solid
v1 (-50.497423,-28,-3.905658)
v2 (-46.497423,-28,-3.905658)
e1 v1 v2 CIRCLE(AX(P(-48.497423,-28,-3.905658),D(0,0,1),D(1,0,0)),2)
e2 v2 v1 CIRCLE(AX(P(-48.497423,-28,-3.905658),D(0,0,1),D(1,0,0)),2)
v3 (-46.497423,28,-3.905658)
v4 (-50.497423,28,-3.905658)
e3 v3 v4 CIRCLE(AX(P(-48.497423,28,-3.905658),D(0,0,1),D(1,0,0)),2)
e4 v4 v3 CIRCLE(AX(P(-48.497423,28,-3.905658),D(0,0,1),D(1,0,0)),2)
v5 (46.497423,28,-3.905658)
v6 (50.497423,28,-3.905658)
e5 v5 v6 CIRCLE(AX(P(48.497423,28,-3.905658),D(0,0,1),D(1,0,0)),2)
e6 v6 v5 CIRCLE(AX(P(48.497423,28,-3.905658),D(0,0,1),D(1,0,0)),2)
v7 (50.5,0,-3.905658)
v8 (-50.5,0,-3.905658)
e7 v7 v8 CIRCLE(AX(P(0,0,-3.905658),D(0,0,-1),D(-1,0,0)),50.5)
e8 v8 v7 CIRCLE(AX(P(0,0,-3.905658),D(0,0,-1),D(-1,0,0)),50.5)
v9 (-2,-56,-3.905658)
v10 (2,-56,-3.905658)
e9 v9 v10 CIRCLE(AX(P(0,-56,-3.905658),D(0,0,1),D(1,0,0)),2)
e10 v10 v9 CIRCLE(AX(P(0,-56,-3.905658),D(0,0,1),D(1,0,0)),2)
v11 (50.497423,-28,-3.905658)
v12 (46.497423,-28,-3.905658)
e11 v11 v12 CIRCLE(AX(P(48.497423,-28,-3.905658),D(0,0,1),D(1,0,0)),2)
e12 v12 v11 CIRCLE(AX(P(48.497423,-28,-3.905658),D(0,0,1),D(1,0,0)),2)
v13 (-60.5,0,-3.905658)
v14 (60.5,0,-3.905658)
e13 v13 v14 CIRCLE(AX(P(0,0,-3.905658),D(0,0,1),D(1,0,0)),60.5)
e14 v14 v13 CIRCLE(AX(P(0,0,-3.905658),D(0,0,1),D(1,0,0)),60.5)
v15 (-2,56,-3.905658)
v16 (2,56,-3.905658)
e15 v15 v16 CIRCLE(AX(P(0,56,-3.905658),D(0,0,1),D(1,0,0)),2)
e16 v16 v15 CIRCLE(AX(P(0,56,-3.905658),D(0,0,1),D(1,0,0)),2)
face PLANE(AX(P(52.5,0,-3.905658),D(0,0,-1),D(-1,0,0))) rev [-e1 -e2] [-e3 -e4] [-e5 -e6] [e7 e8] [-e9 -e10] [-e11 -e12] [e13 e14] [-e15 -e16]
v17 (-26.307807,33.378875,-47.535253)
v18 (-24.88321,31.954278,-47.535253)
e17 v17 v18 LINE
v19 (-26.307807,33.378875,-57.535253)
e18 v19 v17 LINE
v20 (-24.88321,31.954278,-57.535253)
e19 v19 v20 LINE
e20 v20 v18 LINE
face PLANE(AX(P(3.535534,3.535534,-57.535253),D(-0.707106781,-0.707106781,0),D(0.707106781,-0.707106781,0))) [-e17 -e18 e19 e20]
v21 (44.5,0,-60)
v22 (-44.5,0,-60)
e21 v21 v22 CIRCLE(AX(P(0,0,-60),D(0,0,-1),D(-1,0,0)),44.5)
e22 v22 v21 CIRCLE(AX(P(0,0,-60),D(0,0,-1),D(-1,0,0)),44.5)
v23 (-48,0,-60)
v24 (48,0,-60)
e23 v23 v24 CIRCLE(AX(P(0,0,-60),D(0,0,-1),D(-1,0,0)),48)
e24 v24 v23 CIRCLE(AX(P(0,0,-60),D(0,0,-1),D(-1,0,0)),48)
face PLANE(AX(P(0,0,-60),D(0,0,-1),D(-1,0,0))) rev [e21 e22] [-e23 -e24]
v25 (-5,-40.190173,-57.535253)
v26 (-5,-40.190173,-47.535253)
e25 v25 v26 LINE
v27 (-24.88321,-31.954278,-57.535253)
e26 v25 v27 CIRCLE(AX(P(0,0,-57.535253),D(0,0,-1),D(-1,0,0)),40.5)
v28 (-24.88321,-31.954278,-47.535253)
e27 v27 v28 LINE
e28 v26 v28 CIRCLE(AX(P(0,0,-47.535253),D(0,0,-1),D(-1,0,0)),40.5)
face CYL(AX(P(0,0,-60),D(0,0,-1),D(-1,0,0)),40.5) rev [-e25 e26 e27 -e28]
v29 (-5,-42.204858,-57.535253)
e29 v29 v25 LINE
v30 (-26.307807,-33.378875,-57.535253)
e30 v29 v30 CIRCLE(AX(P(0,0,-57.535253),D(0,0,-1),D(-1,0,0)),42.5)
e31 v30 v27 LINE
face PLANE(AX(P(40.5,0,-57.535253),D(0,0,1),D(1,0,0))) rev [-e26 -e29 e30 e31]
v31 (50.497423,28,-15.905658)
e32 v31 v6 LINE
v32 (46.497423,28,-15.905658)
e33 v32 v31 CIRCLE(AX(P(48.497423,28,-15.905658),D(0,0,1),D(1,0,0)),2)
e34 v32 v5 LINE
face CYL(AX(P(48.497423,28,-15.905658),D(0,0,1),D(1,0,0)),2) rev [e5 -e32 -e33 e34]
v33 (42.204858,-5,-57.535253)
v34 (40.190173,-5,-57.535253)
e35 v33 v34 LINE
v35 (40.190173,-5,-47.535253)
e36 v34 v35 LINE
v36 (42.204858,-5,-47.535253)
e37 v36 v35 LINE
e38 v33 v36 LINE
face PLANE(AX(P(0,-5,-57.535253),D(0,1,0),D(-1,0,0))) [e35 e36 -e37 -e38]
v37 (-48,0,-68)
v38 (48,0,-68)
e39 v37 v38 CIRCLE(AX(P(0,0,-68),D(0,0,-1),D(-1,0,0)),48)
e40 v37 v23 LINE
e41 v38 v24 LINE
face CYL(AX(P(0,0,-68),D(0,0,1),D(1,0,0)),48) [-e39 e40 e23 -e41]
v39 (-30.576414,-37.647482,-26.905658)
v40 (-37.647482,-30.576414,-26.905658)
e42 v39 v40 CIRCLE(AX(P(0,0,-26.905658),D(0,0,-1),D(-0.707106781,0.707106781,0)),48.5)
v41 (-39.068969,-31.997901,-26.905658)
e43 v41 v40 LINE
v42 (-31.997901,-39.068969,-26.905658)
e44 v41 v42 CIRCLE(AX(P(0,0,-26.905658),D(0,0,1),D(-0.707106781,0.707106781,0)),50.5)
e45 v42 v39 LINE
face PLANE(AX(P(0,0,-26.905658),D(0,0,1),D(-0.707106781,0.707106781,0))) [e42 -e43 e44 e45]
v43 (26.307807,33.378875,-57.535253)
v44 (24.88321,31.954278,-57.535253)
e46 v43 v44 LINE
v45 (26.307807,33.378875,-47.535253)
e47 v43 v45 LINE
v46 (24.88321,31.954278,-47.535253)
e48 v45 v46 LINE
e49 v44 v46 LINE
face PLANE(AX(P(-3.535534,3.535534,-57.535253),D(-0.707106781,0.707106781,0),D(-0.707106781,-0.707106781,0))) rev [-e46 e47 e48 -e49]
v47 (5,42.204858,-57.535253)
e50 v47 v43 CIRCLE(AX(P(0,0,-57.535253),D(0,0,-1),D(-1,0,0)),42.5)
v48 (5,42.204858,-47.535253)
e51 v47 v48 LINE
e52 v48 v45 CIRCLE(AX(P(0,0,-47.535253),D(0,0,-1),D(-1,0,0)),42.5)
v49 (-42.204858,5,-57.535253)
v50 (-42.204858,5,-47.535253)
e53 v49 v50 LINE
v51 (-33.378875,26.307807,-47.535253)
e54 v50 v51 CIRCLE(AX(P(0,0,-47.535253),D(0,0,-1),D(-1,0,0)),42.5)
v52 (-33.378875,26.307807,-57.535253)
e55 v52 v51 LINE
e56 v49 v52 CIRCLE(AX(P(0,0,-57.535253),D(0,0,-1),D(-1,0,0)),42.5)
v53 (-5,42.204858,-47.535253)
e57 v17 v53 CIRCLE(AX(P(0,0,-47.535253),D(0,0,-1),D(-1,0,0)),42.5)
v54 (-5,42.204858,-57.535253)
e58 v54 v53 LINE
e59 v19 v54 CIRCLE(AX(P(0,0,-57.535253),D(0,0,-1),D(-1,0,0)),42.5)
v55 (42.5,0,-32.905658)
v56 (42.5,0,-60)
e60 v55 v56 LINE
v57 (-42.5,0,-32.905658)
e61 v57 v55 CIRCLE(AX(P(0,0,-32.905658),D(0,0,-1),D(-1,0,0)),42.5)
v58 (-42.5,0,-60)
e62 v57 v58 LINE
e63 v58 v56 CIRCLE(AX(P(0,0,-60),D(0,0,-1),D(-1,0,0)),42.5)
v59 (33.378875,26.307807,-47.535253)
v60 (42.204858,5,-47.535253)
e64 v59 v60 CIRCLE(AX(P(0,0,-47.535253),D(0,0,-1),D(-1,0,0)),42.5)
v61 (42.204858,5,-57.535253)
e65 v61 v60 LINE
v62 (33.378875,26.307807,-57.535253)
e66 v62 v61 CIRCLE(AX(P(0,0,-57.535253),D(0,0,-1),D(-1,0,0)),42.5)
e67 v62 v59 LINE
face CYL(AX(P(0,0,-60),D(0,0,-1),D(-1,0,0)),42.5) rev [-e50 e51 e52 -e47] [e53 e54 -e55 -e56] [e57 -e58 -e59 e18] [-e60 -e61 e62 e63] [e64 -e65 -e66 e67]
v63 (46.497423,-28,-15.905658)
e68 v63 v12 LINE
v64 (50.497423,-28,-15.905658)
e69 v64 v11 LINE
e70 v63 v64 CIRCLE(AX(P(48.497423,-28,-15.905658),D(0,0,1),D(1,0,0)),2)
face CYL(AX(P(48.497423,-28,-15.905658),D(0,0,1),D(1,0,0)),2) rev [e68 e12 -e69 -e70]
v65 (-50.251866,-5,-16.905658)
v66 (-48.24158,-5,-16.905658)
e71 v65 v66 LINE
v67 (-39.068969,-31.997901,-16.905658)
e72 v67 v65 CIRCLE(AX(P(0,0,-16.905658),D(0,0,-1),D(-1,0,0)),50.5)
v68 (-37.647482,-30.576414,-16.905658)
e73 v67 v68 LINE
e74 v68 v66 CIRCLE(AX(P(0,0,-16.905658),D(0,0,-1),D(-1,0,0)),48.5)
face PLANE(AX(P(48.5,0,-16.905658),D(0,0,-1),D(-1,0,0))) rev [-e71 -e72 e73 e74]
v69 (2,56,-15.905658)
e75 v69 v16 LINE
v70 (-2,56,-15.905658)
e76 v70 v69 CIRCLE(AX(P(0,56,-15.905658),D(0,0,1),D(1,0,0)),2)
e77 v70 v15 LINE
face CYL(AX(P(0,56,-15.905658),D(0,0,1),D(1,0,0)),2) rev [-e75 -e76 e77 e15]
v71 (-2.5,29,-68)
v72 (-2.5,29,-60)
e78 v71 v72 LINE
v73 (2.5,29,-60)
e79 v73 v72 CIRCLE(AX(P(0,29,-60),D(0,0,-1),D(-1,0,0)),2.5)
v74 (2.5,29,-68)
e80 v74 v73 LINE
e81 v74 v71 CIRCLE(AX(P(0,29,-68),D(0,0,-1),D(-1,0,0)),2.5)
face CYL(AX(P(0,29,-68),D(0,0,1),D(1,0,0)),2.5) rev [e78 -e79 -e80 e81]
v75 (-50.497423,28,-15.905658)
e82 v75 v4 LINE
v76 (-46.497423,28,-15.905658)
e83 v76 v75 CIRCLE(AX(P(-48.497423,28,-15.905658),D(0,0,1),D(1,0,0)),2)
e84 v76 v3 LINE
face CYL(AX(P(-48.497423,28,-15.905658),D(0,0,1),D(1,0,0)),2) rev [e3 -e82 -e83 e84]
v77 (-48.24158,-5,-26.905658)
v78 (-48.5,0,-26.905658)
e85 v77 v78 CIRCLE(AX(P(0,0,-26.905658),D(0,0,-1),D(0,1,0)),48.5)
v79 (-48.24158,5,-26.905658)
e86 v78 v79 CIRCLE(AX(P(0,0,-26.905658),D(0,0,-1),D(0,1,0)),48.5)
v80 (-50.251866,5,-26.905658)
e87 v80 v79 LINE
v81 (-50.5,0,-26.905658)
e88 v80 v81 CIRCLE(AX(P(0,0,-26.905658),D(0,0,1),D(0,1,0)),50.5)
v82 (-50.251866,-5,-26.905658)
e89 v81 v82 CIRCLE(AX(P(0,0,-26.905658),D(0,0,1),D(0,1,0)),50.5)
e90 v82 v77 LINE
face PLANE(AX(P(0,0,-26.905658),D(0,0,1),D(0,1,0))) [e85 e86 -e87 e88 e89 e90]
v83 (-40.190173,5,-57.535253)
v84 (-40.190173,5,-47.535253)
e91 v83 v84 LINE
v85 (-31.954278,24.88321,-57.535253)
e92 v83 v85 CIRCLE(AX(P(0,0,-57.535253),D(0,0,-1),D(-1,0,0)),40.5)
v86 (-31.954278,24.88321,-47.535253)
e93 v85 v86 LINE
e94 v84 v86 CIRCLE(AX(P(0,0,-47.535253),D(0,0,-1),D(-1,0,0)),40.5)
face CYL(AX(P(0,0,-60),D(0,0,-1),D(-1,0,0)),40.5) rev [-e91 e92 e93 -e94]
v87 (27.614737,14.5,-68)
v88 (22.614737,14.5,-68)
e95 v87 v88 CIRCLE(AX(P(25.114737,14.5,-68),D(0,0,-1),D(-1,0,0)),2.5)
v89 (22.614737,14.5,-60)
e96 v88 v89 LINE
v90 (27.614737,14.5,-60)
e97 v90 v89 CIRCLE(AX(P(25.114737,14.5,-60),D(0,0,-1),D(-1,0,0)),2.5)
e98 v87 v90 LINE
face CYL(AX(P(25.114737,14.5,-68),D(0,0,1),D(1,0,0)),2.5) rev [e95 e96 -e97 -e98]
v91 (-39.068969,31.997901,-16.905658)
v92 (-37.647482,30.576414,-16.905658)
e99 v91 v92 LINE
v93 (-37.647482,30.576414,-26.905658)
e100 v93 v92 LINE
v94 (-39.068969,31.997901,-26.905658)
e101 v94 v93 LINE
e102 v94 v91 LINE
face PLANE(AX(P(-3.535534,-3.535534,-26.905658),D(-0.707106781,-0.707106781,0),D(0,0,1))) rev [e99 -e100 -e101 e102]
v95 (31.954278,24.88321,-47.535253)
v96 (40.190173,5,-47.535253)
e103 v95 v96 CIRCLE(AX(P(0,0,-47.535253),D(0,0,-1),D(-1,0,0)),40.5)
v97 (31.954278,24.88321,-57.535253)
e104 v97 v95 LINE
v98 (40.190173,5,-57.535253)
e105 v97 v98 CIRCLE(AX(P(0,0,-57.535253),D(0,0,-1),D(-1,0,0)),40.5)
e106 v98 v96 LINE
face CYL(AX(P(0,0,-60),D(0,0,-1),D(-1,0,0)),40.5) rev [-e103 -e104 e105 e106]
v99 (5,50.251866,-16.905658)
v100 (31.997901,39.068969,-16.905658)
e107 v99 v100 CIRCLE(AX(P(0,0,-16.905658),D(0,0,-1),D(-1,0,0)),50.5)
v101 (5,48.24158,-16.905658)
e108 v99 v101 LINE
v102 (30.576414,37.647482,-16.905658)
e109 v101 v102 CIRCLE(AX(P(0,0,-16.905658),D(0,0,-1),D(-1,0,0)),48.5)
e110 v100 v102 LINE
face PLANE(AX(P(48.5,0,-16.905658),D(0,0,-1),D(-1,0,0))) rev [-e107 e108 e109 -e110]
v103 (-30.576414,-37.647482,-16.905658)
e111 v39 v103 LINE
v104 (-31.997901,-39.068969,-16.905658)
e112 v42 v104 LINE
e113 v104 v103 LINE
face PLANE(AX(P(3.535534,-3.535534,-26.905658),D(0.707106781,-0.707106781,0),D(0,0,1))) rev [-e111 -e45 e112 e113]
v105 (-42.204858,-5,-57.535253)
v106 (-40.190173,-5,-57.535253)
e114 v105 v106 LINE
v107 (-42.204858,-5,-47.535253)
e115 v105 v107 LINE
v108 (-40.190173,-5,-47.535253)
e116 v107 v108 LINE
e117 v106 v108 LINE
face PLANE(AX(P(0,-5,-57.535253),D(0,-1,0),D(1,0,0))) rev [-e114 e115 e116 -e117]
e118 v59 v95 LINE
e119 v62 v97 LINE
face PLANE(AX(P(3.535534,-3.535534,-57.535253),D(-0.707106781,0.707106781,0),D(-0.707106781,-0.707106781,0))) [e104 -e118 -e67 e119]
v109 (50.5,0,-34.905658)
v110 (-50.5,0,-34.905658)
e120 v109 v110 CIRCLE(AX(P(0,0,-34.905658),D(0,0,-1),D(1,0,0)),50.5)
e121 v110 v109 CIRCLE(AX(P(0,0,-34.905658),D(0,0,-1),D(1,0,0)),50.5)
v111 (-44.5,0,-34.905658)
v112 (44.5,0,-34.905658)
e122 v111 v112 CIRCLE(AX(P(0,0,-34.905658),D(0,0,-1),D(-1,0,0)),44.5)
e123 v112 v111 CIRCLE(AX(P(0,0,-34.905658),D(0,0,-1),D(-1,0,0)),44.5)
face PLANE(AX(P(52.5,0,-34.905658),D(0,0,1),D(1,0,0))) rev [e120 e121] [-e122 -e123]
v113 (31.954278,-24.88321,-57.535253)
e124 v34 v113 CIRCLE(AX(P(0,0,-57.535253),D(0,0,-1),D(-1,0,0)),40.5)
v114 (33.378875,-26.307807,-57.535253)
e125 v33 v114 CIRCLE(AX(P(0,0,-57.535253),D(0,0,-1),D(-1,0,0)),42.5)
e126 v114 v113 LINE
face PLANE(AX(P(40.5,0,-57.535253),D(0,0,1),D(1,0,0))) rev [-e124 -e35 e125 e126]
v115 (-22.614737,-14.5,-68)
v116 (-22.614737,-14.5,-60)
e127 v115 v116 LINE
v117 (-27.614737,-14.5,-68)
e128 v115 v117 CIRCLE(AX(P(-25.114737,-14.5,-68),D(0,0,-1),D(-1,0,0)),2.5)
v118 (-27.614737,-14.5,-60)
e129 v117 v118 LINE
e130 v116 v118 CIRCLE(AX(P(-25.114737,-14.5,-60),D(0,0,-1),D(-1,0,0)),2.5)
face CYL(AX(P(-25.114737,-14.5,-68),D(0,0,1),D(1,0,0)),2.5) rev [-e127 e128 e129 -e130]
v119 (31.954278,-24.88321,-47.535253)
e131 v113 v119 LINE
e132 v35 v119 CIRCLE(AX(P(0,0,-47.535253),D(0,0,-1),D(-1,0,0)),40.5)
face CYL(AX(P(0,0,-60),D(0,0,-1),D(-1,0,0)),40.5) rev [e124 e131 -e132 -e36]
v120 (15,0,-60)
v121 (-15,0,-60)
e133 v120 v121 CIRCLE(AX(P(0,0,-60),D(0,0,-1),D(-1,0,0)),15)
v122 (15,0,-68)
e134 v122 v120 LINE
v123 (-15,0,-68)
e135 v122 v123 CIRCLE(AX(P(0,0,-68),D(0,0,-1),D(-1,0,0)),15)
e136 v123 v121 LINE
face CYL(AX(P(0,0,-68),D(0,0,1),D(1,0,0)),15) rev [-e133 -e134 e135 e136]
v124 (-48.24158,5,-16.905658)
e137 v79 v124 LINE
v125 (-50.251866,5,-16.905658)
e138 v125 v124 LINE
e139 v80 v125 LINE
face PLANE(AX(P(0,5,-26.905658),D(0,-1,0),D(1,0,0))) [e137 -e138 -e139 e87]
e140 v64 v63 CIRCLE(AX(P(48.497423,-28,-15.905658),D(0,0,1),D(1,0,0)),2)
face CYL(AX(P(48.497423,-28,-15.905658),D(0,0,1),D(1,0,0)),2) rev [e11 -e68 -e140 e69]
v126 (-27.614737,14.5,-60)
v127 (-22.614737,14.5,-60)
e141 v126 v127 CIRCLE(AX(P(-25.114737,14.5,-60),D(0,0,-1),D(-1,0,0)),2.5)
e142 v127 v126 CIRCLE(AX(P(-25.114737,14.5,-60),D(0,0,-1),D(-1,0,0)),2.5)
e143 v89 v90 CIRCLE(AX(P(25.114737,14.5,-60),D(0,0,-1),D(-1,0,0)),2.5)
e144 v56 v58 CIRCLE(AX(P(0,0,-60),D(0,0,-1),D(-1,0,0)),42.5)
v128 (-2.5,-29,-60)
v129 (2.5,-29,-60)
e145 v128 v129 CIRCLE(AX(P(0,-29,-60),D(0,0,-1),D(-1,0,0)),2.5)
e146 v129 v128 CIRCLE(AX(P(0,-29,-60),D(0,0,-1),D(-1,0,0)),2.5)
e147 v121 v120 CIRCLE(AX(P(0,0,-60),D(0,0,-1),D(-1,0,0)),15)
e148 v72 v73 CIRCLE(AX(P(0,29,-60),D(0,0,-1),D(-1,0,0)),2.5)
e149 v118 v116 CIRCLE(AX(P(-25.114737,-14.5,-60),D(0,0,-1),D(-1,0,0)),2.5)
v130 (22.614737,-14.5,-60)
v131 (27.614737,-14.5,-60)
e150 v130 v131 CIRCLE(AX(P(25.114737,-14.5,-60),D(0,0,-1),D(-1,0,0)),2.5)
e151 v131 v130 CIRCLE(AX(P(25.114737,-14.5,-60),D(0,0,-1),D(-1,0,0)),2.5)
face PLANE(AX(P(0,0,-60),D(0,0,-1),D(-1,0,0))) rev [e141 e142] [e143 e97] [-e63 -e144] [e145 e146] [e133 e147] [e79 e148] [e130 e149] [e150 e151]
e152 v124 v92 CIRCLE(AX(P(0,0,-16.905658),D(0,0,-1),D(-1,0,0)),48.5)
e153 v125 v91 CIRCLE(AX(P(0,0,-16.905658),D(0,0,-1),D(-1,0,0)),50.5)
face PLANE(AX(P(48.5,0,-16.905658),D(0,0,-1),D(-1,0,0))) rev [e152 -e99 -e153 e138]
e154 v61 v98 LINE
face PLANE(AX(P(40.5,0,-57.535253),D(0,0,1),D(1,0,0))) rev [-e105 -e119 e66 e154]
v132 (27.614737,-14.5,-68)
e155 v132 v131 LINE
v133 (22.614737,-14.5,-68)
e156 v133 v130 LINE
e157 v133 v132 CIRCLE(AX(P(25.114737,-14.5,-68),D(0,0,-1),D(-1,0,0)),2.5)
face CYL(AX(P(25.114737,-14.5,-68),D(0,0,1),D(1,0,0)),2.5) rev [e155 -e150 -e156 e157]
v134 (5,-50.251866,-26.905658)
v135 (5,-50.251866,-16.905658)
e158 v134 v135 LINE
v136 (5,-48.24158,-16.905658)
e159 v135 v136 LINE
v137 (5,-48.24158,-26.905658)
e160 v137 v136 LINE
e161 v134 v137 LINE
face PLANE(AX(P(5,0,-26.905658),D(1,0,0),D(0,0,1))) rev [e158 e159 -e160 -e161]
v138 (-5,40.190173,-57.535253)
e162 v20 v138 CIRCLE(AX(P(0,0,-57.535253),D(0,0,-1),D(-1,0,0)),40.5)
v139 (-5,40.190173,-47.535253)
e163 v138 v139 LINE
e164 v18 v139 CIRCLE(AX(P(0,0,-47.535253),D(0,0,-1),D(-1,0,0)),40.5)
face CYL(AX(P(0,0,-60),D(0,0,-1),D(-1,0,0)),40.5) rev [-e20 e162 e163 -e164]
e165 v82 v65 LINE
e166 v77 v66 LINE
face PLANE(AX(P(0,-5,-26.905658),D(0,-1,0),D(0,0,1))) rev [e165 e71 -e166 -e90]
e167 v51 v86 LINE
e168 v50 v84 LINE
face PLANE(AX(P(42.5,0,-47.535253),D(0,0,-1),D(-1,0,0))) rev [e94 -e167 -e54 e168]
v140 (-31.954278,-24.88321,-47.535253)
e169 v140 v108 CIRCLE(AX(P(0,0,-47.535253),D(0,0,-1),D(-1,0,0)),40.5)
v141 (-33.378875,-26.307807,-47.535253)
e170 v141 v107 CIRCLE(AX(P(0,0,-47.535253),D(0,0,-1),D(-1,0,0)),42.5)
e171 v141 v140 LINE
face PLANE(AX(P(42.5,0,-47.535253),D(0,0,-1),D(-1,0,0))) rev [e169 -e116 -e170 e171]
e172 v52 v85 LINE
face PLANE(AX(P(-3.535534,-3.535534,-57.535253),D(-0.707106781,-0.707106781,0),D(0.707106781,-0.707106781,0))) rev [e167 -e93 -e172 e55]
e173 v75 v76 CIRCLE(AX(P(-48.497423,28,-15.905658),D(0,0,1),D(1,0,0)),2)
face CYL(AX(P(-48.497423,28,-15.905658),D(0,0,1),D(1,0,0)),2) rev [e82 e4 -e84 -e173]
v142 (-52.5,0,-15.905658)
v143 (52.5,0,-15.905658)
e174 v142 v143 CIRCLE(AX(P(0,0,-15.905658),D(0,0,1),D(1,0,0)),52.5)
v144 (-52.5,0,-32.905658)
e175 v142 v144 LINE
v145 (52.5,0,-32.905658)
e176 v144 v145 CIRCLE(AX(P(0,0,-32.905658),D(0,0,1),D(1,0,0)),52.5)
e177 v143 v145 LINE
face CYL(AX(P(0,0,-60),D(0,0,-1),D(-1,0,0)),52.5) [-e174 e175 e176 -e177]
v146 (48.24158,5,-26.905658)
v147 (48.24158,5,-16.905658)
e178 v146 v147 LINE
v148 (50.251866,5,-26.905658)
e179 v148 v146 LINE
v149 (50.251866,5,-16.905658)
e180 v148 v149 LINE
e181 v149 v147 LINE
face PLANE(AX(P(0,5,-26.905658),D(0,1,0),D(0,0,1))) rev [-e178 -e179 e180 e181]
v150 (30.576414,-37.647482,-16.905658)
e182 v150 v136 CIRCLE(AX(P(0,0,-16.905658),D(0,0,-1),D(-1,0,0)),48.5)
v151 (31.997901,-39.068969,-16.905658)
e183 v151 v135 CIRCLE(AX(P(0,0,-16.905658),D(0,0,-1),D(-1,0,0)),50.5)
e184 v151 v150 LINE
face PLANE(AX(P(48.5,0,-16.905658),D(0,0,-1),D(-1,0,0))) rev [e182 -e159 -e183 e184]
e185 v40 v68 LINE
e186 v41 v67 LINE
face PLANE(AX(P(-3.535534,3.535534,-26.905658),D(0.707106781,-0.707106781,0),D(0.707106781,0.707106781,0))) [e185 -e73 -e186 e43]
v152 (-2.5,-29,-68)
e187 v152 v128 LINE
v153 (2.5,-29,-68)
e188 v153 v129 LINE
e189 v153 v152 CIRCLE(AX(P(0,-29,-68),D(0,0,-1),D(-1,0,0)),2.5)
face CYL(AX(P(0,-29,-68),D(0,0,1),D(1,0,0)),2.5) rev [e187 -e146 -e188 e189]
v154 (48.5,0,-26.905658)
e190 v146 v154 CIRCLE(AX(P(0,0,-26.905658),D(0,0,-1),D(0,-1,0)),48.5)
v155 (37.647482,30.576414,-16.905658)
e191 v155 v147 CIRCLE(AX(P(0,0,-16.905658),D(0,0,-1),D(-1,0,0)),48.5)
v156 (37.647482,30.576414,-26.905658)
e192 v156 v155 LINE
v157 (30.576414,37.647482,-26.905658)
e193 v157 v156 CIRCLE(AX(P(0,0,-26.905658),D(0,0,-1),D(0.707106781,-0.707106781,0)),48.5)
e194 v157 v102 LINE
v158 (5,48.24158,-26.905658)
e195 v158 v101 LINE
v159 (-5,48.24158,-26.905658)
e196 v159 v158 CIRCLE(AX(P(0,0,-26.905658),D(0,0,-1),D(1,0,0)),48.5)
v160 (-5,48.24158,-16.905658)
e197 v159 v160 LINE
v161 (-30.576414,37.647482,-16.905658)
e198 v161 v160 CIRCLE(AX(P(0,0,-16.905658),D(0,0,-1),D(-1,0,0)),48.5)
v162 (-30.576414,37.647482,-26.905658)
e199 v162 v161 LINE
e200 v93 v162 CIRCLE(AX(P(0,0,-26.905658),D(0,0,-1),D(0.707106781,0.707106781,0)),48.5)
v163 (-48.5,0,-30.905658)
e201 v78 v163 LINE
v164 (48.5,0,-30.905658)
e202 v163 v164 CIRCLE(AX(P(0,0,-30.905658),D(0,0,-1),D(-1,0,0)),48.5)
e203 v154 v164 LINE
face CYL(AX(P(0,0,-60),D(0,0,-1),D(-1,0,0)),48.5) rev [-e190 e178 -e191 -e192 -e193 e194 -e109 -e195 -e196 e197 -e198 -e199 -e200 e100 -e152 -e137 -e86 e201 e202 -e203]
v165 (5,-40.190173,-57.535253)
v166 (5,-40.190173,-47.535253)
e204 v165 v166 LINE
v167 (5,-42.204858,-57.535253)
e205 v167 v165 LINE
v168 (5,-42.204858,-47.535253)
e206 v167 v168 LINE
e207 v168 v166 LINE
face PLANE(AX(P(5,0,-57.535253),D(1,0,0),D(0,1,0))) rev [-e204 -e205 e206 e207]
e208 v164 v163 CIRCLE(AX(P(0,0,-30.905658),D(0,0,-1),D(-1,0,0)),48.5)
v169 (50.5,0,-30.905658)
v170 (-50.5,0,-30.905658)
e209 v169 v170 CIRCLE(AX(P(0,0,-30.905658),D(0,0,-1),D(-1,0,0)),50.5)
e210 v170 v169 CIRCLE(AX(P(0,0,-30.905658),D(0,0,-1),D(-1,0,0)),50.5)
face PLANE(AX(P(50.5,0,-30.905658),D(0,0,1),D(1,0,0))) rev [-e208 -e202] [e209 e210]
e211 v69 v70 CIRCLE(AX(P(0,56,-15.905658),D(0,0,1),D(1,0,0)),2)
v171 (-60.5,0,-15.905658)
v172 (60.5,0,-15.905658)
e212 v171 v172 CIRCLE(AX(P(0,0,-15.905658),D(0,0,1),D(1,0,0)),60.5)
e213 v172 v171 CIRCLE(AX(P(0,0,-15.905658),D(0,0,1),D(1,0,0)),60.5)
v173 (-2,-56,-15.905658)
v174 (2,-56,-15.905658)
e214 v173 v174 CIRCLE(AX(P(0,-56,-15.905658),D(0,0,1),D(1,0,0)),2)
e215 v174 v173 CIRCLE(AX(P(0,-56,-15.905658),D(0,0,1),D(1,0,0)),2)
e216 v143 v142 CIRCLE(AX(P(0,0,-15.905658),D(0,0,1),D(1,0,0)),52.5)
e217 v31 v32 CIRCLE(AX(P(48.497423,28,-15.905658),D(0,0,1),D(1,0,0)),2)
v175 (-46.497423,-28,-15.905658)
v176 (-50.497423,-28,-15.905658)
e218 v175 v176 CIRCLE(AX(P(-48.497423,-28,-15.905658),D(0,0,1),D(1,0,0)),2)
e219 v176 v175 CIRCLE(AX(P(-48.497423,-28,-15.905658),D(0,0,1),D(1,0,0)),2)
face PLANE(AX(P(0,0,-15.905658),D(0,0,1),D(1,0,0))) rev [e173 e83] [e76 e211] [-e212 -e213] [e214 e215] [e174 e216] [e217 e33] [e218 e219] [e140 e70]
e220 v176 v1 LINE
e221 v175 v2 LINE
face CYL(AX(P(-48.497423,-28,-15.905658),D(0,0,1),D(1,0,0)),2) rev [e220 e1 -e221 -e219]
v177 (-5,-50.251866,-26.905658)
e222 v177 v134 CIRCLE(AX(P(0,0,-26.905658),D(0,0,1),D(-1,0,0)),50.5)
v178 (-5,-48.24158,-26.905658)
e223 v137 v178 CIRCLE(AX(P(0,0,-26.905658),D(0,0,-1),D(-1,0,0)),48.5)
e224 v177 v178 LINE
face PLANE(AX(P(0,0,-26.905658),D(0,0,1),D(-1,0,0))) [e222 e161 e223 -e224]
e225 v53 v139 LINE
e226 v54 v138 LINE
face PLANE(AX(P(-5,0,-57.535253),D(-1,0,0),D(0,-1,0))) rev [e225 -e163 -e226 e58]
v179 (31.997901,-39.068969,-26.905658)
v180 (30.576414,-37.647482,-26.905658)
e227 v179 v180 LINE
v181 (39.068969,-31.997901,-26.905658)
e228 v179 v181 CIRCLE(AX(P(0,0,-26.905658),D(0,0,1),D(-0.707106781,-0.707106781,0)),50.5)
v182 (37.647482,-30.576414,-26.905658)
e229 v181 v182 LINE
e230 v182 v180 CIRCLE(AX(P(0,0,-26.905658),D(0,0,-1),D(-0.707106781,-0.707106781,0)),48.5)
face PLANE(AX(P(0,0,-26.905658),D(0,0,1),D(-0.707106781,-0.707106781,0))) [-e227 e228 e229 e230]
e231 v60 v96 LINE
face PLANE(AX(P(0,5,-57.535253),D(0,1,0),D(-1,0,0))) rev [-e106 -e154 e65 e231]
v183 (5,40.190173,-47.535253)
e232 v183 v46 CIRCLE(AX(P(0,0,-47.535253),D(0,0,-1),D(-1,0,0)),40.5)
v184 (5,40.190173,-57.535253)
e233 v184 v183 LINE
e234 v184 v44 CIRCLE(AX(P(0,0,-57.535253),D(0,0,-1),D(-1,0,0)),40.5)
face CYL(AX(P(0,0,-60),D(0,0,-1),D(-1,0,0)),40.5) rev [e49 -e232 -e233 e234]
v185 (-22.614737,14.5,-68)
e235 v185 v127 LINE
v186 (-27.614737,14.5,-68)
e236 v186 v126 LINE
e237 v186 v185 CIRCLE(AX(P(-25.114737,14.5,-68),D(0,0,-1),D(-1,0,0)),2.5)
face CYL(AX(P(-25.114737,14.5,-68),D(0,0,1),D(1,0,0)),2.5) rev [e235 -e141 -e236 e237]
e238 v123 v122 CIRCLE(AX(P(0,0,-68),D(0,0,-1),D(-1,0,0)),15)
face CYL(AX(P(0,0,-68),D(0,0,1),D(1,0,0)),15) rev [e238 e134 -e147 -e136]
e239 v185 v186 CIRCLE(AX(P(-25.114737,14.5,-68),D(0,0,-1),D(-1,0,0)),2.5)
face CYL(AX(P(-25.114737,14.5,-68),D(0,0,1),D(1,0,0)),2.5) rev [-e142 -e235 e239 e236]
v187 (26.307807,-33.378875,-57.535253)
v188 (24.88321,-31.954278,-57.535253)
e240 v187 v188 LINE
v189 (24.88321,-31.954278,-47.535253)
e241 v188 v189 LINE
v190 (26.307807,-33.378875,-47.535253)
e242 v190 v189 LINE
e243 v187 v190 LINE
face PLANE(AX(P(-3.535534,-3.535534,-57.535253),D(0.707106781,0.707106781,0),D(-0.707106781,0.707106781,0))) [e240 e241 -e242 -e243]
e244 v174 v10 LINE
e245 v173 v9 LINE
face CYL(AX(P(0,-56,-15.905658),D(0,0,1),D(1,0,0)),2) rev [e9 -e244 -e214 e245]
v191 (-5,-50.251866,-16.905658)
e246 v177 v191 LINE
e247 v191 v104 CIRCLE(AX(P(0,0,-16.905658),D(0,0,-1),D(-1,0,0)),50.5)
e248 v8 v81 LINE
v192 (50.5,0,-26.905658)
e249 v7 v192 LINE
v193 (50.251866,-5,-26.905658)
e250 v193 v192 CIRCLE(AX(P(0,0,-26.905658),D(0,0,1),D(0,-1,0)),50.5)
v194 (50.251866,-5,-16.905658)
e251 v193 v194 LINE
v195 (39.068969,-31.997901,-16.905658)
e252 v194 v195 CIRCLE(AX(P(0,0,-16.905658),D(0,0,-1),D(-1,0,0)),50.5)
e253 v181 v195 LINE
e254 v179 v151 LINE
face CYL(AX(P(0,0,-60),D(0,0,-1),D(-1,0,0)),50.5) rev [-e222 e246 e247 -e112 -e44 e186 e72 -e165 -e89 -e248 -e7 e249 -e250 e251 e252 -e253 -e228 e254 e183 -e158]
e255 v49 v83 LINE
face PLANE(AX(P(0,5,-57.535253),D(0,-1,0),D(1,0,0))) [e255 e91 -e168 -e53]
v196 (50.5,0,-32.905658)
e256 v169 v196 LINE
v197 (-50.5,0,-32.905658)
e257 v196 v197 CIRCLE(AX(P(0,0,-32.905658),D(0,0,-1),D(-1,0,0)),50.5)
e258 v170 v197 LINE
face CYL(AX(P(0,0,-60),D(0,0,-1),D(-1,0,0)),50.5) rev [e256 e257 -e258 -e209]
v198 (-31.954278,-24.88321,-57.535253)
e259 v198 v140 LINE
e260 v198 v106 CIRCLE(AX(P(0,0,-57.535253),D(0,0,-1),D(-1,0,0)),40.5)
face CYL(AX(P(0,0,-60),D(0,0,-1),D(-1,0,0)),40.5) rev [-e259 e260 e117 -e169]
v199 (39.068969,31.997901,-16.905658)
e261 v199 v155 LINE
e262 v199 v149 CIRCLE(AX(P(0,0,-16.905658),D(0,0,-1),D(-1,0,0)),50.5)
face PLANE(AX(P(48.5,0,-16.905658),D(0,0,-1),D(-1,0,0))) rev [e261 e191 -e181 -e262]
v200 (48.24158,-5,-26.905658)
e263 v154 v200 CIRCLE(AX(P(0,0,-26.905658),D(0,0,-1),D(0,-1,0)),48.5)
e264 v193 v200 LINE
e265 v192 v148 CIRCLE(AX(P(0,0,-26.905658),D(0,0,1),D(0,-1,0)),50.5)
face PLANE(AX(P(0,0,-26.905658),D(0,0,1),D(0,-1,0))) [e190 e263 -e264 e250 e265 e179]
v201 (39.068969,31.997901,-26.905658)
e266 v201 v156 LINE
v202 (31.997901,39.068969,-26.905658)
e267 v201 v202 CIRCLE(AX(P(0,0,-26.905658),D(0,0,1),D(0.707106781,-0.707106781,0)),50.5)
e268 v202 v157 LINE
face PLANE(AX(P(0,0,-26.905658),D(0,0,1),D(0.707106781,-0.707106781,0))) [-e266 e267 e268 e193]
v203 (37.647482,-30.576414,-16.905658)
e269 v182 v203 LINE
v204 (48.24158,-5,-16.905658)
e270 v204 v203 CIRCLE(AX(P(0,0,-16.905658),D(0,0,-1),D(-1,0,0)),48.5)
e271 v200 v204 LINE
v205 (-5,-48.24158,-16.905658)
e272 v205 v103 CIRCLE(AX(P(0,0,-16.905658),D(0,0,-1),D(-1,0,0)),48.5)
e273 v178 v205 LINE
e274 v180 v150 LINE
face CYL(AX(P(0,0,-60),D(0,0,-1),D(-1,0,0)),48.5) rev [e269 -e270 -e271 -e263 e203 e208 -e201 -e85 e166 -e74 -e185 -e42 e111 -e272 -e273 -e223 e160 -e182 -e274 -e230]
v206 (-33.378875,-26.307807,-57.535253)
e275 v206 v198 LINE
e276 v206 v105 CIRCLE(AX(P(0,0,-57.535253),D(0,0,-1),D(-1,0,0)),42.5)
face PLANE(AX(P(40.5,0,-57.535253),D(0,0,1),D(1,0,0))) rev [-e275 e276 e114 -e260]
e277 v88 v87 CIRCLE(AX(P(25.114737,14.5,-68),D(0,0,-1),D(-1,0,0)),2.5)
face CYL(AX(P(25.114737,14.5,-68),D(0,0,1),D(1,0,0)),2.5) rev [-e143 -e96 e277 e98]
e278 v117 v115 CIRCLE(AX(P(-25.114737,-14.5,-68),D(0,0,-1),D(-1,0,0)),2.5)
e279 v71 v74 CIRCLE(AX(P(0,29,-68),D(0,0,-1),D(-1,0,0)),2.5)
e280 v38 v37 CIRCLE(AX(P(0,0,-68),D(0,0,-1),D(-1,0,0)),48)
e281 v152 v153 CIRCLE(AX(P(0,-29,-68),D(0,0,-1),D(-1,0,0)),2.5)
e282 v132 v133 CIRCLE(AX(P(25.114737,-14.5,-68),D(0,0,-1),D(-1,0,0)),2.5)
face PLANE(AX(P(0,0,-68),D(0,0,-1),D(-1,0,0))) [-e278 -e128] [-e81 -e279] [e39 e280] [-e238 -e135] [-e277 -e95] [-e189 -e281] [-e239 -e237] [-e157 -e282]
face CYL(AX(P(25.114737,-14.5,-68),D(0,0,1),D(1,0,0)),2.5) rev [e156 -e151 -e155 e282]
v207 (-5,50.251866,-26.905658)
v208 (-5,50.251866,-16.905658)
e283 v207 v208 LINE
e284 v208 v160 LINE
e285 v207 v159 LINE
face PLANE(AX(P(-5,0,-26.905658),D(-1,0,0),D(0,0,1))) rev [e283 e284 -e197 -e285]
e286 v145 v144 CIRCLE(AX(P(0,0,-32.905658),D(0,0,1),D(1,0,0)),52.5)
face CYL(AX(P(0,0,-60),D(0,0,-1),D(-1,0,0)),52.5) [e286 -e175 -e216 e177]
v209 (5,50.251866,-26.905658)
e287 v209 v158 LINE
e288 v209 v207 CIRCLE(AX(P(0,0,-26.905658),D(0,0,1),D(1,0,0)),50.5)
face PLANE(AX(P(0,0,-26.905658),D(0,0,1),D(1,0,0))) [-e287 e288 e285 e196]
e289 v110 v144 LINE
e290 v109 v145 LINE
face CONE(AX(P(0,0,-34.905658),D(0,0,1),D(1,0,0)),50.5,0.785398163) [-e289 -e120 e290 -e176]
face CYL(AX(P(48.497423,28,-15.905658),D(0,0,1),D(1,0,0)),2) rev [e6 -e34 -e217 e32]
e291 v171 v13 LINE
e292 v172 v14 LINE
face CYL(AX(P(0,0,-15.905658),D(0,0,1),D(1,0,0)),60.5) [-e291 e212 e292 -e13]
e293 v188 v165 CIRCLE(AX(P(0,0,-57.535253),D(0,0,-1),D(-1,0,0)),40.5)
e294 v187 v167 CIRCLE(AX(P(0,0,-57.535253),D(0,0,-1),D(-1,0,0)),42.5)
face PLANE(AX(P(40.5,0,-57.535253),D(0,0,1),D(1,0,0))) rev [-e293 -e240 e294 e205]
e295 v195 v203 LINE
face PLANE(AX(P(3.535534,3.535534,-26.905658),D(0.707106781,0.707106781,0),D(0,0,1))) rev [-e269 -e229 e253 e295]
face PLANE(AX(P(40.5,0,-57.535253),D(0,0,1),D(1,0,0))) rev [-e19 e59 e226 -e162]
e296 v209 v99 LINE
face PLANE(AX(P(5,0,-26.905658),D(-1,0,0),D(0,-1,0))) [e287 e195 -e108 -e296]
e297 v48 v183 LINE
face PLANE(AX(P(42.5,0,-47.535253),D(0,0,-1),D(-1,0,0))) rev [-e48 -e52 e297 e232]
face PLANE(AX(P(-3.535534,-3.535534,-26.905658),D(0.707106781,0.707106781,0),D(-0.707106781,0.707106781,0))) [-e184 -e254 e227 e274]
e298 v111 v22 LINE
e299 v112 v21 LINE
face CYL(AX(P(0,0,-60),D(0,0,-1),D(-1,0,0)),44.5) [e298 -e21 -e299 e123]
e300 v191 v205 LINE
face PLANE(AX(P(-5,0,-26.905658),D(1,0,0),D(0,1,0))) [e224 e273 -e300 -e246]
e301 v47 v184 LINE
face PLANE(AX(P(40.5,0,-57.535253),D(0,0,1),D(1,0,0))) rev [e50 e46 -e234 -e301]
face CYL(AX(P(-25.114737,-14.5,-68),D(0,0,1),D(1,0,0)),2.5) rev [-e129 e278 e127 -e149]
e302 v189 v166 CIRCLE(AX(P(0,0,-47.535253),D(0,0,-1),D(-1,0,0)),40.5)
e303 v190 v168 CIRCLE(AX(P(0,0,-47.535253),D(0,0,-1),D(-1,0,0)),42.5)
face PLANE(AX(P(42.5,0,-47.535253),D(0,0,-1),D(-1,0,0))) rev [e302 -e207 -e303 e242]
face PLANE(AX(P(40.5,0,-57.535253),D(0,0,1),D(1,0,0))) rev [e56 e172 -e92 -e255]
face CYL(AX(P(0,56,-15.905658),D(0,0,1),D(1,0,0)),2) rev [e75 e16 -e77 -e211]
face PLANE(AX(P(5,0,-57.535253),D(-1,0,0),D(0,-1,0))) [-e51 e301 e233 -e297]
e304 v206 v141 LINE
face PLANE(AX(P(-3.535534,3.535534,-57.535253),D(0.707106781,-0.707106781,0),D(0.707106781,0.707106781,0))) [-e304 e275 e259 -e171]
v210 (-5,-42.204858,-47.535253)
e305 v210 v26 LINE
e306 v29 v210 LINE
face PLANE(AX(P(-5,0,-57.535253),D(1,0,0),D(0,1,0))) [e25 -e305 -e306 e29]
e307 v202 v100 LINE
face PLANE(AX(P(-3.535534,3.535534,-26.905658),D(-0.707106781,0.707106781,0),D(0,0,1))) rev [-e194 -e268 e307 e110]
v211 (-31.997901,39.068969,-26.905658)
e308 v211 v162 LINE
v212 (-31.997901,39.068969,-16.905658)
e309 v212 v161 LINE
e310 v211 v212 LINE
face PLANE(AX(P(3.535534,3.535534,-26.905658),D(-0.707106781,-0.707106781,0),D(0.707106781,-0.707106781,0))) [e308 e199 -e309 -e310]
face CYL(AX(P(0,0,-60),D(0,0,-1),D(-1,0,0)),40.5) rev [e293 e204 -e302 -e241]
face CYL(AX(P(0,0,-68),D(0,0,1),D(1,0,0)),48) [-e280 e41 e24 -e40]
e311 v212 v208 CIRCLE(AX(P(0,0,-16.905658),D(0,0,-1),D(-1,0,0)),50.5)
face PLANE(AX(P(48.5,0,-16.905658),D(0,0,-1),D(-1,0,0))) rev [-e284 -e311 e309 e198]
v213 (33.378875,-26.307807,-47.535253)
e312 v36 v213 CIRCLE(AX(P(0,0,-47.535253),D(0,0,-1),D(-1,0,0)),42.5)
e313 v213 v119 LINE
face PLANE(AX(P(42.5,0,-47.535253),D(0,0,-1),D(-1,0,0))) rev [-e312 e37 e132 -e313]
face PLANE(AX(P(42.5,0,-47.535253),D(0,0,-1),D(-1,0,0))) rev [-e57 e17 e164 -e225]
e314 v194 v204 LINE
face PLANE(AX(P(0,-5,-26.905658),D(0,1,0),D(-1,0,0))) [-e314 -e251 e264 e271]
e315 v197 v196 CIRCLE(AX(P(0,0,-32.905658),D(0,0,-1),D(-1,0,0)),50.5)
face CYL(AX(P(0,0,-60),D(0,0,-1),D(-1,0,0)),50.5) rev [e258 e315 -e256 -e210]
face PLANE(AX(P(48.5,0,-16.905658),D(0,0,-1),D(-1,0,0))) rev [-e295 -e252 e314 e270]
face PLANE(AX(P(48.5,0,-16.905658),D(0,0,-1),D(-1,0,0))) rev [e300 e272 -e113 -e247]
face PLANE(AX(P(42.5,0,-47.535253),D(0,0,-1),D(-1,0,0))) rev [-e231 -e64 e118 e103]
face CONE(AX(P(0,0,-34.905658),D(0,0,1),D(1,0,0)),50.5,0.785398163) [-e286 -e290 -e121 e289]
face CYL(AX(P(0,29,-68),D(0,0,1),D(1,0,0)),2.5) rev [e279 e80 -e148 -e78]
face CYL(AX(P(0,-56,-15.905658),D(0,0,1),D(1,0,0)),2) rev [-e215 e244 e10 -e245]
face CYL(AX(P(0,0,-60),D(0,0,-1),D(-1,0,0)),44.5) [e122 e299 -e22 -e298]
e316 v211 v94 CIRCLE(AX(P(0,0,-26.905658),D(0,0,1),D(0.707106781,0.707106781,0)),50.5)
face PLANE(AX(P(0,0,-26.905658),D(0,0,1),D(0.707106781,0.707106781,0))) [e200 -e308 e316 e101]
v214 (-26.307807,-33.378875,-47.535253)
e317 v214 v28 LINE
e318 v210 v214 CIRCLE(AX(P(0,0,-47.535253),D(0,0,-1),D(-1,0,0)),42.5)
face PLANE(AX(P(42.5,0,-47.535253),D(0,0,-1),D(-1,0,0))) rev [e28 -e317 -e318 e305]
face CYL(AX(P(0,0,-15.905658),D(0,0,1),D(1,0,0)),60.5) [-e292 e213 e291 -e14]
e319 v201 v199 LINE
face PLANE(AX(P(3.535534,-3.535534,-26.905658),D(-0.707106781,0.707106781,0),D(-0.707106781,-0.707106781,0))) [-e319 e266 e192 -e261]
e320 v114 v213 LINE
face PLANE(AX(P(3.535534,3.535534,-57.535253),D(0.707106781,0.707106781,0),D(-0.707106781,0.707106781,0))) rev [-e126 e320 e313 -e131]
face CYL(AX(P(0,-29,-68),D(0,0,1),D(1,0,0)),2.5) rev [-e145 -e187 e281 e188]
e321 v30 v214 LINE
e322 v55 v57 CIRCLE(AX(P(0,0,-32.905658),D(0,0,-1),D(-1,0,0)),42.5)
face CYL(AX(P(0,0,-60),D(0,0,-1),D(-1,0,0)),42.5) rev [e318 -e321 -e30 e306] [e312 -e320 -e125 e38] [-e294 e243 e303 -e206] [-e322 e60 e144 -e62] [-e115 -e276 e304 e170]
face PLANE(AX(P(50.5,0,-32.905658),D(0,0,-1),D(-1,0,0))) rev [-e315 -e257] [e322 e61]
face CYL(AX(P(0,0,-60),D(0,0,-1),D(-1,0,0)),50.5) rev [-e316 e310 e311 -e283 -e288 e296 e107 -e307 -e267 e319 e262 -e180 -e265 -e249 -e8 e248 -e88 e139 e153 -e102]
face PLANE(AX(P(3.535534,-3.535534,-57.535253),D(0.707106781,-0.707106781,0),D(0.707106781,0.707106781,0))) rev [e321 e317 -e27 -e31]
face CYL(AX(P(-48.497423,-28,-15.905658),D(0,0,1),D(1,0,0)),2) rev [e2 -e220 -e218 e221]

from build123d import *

# Parameters (mm, degrees)
CUT_EXTRUDE2_START  = -10
SKETCH3_R           = 40.5
CUT_EXTRUDE2_DEPTH  = 10
CUT_EXTRUDE3_START  = -10
CUT_EXTRUDE3_DEPTH  = 10
CIRPATTERN5_COUNT   = 8
CHAMFER1_SIZE       = 2
SKETCH4_R           = 48
SKETCH4_R_2         = 15
SKETCH4_R_3         = 2.5
BOSS_EXTRUDE1_DEPTH = 8
SKETCH7_R           = 60.5
SKETCH7_R_2         = 52.5
SKETCH7_R_3         = 2
BOSS_EXTRUDE2_DEPTH = 12


with BuildPart() as part:
    # Sketch1 → Revolve1 (revolve)
    with BuildSketch(Plane(origin=(0, 0, 0), x_dir=(1, 0, 0), z_dir=(0, 1, 0)), mode=Mode.PRIVATE) as revolve1_sk:
        Polygon((50.5, 3.905657953), (50.5, 16.905657953), (48.5, 16.905657953), (48.5, 30.905657953), (50.5, 30.905657953), (50.5, 32.905657953), (42.5, 32.905657953), (42.5, 47.535252784), (40.5, 47.535252784), (40.5, 57.535252784), (42.5, 57.535252784), (42.5, 60), (44.5, 60), (44.5, 34.905657953), (52.5, 34.905657953), (52.5, 3.905657953), align=None)
    revolve(revolve1_sk.sketch.rotate(Axis((0, 0, -60), (0, 0, 1)), 180), axis=Axis((0, 0, -60), (0, 0, 1)))

    # Sketch3 → Cut-Extrude2 (cut)
    with BuildSketch(Plane.XY.offset(-47.535252784).offset(CUT_EXTRUDE2_START)):
        with BuildLine():
            ThreePointArc((5, 42.20485754), (0, 42.5), (-5, 42.20485754))
            Line((-5, 42.20485754), (-5, 40.190172928))
            ThreePointArc((-5, 40.190172928), (0, 40.5), (5, 40.190172928))
            Line((5, 40.190172928), (5, 42.20485754))
        make_face()
        with BuildLine():
            ThreePointArc((33.378874872, 26.30780706), (30.0520382, 30.0520382), (26.30780706, 33.378874872))
            Line((26.30780706, 33.378874872), (24.883209909, 31.954277721))
            ThreePointArc((24.883209909, 31.954277721), (28.637824638, 28.637824638), (31.954277721, 24.883209909))
            Line((31.954277721, 24.883209909), (33.378874872, 26.30780706))
        make_face()
        with BuildLine():
            ThreePointArc((42.5, 0), (42.426150223, 2.504351666), (42.20485754, 5))
            Line((42.20485754, 5), (40.190172928, 5))
            ThreePointArc((40.190172928, 5), (40.422469022, 2.504795042), (40.5, 0))
            ThreePointArc((40.5, 0), (40.422469022, -2.504795042), (40.190172928, -5))
            Line((40.190172928, -5), (42.20485754, -5))
            ThreePointArc((42.20485754, -5), (42.426150223, -2.504351666), (42.5, 0))
        make_face()
        with BuildLine():
            ThreePointArc((26.30780706, -33.378874872), (30.0520382, -30.0520382), (33.378874872, -26.30780706))
            Line((33.378874872, -26.30780706), (31.954277721, -24.883209909))
            ThreePointArc((31.954277721, -24.883209909), (28.637824638, -28.637824638), (24.883209909, -31.954277721))
            Line((24.883209909, -31.954277721), (26.30780706, -33.378874872))
        make_face()
        with BuildLine():
            Line((-5, -40.190172928), (-5, -42.20485754))
            ThreePointArc((-5, -42.20485754), (0, -42.5), (5, -42.20485754))
            Line((5, -42.20485754), (5, -40.190172928))
            ThreePointArc((5, -40.190172928), (0, -40.5), (-5, -40.190172928))
        make_face()
        with BuildLine():
            Line((-31.954277721, -24.883209909), (-33.378874872, -26.30780706))
            ThreePointArc((-33.378874872, -26.30780706), (-30.0520382, -30.0520382), (-26.30780706, -33.378874872))
            Line((-26.30780706, -33.378874872), (-24.883209909, -31.954277721))
            ThreePointArc((-24.883209909, -31.954277721), (-28.637824638, -28.637824638), (-31.954277721, -24.883209909))
        make_face()
        with BuildLine():
            Line((-40.190172928, 5), (-42.20485754, 5))
            ThreePointArc((-42.20485754, 5), (-42.5, 0), (-42.20485754, -5))
            Line((-42.20485754, -5), (-40.190172928, -5))
            ThreePointArc((-40.190172928, -5), (-40.5, 0), (-40.190172928, 5))
        make_face()
        with BuildLine():
            Line((-24.883209909, 31.954277721), (-26.30780706, 33.378874872))
            ThreePointArc((-26.30780706, 33.378874872), (-30.0520382, 30.0520382), (-33.378874872, 26.30780706))
            Line((-33.378874872, 26.30780706), (-31.954277721, 24.883209909))
            ThreePointArc((-31.954277721, 24.883209909), (-28.637824638, 28.637824638), (-24.883209909, 31.954277721))
        make_face()
        Circle(SKETCH3_R)
    extrude(amount=CUT_EXTRUDE2_DEPTH, mode=Mode.SUBTRACT)

    # Sketch2 → Cut-Extrude3 (cut)
    with BuildSketch(Plane.XY.offset(-16.905657953).offset(CUT_EXTRUDE3_START)):
        with BuildLine():
            ThreePointArc((5, 50.251865637), (0, 50.5), (-5, 50.251865637))
            Line((-5, 50.251865637), (-5, 48.241579576))
            ThreePointArc((-5, 48.241579576), (0, 48.5), (5, 48.241579576))
            Line((5, 48.241579576), (5, 50.251865637))
        make_face()
    cut_extrude3 = extrude(amount=CUT_EXTRUDE3_DEPTH, mode=Mode.SUBTRACT)

    # CirPattern5: Cut-Extrude3 ×8 about axis
    cirpattern5_axis = Axis((0, 0, 0), (0, 0, 1))
    for i in range(1, CIRPATTERN5_COUNT):
        add(cut_extrude3.rotate(cirpattern5_axis, i * 360 / CIRPATTERN5_COUNT), mode=Mode.SUBTRACT)

    # Chamfer1
    chamfer1_edges = [part.edges().sort_by_distance(p)[0] for p in [
        (52.5, 0, -34.905657953),
    ]]
    chamfer(chamfer1_edges, length=CHAMFER1_SIZE)

    # Sketch4 → Boss-Extrude1 (add)
    with BuildSketch(Plane(origin=(0, 0, -60), x_dir=(-1, 0, 0), z_dir=(0, 0, -1))):
        Circle(SKETCH4_R)
        Circle(SKETCH4_R_2, mode=Mode.SUBTRACT)
        with Locations((0, 29)):
            Circle(SKETCH4_R_3, mode=Mode.SUBTRACT)
        with Locations((25.11473671, 14.5)):
            Circle(SKETCH4_R_3, mode=Mode.SUBTRACT)
        with Locations((25.11473671, -14.5)):
            Circle(SKETCH4_R_3, mode=Mode.SUBTRACT)
        with Locations((0, -29)):
            Circle(SKETCH4_R_3, mode=Mode.SUBTRACT)
        with Locations((-25.11473671, -14.5)):
            Circle(SKETCH4_R_3, mode=Mode.SUBTRACT)
        with Locations((-25.11473671, 14.5)):
            Circle(SKETCH4_R_3, mode=Mode.SUBTRACT)
    extrude(amount=BOSS_EXTRUDE1_DEPTH)

    # Sketch7 → Boss-Extrude2 (add)
    with BuildSketch(Plane.XY.offset(-3.905657953)):
        Circle(SKETCH7_R)
        Circle(SKETCH7_R_2, mode=Mode.SUBTRACT)
        with Locations((0, 56)):
            Circle(SKETCH7_R_3, mode=Mode.SUBTRACT)
        with Locations((48.497422612, 28)):
            Circle(SKETCH7_R_3, mode=Mode.SUBTRACT)
        with Locations((48.497422612, -28)):
            Circle(SKETCH7_R_3, mode=Mode.SUBTRACT)
        with Locations((0, -56)):
            Circle(SKETCH7_R_3, mode=Mode.SUBTRACT)
        with Locations((-48.497422612, -28)):
            Circle(SKETCH7_R_3, mode=Mode.SUBTRACT)
        with Locations((-48.497422612, 28)):
            Circle(SKETCH7_R_3, mode=Mode.SUBTRACT)
    extrude(amount=-BOSS_EXTRUDE2_DEPTH)


solid = part.part
